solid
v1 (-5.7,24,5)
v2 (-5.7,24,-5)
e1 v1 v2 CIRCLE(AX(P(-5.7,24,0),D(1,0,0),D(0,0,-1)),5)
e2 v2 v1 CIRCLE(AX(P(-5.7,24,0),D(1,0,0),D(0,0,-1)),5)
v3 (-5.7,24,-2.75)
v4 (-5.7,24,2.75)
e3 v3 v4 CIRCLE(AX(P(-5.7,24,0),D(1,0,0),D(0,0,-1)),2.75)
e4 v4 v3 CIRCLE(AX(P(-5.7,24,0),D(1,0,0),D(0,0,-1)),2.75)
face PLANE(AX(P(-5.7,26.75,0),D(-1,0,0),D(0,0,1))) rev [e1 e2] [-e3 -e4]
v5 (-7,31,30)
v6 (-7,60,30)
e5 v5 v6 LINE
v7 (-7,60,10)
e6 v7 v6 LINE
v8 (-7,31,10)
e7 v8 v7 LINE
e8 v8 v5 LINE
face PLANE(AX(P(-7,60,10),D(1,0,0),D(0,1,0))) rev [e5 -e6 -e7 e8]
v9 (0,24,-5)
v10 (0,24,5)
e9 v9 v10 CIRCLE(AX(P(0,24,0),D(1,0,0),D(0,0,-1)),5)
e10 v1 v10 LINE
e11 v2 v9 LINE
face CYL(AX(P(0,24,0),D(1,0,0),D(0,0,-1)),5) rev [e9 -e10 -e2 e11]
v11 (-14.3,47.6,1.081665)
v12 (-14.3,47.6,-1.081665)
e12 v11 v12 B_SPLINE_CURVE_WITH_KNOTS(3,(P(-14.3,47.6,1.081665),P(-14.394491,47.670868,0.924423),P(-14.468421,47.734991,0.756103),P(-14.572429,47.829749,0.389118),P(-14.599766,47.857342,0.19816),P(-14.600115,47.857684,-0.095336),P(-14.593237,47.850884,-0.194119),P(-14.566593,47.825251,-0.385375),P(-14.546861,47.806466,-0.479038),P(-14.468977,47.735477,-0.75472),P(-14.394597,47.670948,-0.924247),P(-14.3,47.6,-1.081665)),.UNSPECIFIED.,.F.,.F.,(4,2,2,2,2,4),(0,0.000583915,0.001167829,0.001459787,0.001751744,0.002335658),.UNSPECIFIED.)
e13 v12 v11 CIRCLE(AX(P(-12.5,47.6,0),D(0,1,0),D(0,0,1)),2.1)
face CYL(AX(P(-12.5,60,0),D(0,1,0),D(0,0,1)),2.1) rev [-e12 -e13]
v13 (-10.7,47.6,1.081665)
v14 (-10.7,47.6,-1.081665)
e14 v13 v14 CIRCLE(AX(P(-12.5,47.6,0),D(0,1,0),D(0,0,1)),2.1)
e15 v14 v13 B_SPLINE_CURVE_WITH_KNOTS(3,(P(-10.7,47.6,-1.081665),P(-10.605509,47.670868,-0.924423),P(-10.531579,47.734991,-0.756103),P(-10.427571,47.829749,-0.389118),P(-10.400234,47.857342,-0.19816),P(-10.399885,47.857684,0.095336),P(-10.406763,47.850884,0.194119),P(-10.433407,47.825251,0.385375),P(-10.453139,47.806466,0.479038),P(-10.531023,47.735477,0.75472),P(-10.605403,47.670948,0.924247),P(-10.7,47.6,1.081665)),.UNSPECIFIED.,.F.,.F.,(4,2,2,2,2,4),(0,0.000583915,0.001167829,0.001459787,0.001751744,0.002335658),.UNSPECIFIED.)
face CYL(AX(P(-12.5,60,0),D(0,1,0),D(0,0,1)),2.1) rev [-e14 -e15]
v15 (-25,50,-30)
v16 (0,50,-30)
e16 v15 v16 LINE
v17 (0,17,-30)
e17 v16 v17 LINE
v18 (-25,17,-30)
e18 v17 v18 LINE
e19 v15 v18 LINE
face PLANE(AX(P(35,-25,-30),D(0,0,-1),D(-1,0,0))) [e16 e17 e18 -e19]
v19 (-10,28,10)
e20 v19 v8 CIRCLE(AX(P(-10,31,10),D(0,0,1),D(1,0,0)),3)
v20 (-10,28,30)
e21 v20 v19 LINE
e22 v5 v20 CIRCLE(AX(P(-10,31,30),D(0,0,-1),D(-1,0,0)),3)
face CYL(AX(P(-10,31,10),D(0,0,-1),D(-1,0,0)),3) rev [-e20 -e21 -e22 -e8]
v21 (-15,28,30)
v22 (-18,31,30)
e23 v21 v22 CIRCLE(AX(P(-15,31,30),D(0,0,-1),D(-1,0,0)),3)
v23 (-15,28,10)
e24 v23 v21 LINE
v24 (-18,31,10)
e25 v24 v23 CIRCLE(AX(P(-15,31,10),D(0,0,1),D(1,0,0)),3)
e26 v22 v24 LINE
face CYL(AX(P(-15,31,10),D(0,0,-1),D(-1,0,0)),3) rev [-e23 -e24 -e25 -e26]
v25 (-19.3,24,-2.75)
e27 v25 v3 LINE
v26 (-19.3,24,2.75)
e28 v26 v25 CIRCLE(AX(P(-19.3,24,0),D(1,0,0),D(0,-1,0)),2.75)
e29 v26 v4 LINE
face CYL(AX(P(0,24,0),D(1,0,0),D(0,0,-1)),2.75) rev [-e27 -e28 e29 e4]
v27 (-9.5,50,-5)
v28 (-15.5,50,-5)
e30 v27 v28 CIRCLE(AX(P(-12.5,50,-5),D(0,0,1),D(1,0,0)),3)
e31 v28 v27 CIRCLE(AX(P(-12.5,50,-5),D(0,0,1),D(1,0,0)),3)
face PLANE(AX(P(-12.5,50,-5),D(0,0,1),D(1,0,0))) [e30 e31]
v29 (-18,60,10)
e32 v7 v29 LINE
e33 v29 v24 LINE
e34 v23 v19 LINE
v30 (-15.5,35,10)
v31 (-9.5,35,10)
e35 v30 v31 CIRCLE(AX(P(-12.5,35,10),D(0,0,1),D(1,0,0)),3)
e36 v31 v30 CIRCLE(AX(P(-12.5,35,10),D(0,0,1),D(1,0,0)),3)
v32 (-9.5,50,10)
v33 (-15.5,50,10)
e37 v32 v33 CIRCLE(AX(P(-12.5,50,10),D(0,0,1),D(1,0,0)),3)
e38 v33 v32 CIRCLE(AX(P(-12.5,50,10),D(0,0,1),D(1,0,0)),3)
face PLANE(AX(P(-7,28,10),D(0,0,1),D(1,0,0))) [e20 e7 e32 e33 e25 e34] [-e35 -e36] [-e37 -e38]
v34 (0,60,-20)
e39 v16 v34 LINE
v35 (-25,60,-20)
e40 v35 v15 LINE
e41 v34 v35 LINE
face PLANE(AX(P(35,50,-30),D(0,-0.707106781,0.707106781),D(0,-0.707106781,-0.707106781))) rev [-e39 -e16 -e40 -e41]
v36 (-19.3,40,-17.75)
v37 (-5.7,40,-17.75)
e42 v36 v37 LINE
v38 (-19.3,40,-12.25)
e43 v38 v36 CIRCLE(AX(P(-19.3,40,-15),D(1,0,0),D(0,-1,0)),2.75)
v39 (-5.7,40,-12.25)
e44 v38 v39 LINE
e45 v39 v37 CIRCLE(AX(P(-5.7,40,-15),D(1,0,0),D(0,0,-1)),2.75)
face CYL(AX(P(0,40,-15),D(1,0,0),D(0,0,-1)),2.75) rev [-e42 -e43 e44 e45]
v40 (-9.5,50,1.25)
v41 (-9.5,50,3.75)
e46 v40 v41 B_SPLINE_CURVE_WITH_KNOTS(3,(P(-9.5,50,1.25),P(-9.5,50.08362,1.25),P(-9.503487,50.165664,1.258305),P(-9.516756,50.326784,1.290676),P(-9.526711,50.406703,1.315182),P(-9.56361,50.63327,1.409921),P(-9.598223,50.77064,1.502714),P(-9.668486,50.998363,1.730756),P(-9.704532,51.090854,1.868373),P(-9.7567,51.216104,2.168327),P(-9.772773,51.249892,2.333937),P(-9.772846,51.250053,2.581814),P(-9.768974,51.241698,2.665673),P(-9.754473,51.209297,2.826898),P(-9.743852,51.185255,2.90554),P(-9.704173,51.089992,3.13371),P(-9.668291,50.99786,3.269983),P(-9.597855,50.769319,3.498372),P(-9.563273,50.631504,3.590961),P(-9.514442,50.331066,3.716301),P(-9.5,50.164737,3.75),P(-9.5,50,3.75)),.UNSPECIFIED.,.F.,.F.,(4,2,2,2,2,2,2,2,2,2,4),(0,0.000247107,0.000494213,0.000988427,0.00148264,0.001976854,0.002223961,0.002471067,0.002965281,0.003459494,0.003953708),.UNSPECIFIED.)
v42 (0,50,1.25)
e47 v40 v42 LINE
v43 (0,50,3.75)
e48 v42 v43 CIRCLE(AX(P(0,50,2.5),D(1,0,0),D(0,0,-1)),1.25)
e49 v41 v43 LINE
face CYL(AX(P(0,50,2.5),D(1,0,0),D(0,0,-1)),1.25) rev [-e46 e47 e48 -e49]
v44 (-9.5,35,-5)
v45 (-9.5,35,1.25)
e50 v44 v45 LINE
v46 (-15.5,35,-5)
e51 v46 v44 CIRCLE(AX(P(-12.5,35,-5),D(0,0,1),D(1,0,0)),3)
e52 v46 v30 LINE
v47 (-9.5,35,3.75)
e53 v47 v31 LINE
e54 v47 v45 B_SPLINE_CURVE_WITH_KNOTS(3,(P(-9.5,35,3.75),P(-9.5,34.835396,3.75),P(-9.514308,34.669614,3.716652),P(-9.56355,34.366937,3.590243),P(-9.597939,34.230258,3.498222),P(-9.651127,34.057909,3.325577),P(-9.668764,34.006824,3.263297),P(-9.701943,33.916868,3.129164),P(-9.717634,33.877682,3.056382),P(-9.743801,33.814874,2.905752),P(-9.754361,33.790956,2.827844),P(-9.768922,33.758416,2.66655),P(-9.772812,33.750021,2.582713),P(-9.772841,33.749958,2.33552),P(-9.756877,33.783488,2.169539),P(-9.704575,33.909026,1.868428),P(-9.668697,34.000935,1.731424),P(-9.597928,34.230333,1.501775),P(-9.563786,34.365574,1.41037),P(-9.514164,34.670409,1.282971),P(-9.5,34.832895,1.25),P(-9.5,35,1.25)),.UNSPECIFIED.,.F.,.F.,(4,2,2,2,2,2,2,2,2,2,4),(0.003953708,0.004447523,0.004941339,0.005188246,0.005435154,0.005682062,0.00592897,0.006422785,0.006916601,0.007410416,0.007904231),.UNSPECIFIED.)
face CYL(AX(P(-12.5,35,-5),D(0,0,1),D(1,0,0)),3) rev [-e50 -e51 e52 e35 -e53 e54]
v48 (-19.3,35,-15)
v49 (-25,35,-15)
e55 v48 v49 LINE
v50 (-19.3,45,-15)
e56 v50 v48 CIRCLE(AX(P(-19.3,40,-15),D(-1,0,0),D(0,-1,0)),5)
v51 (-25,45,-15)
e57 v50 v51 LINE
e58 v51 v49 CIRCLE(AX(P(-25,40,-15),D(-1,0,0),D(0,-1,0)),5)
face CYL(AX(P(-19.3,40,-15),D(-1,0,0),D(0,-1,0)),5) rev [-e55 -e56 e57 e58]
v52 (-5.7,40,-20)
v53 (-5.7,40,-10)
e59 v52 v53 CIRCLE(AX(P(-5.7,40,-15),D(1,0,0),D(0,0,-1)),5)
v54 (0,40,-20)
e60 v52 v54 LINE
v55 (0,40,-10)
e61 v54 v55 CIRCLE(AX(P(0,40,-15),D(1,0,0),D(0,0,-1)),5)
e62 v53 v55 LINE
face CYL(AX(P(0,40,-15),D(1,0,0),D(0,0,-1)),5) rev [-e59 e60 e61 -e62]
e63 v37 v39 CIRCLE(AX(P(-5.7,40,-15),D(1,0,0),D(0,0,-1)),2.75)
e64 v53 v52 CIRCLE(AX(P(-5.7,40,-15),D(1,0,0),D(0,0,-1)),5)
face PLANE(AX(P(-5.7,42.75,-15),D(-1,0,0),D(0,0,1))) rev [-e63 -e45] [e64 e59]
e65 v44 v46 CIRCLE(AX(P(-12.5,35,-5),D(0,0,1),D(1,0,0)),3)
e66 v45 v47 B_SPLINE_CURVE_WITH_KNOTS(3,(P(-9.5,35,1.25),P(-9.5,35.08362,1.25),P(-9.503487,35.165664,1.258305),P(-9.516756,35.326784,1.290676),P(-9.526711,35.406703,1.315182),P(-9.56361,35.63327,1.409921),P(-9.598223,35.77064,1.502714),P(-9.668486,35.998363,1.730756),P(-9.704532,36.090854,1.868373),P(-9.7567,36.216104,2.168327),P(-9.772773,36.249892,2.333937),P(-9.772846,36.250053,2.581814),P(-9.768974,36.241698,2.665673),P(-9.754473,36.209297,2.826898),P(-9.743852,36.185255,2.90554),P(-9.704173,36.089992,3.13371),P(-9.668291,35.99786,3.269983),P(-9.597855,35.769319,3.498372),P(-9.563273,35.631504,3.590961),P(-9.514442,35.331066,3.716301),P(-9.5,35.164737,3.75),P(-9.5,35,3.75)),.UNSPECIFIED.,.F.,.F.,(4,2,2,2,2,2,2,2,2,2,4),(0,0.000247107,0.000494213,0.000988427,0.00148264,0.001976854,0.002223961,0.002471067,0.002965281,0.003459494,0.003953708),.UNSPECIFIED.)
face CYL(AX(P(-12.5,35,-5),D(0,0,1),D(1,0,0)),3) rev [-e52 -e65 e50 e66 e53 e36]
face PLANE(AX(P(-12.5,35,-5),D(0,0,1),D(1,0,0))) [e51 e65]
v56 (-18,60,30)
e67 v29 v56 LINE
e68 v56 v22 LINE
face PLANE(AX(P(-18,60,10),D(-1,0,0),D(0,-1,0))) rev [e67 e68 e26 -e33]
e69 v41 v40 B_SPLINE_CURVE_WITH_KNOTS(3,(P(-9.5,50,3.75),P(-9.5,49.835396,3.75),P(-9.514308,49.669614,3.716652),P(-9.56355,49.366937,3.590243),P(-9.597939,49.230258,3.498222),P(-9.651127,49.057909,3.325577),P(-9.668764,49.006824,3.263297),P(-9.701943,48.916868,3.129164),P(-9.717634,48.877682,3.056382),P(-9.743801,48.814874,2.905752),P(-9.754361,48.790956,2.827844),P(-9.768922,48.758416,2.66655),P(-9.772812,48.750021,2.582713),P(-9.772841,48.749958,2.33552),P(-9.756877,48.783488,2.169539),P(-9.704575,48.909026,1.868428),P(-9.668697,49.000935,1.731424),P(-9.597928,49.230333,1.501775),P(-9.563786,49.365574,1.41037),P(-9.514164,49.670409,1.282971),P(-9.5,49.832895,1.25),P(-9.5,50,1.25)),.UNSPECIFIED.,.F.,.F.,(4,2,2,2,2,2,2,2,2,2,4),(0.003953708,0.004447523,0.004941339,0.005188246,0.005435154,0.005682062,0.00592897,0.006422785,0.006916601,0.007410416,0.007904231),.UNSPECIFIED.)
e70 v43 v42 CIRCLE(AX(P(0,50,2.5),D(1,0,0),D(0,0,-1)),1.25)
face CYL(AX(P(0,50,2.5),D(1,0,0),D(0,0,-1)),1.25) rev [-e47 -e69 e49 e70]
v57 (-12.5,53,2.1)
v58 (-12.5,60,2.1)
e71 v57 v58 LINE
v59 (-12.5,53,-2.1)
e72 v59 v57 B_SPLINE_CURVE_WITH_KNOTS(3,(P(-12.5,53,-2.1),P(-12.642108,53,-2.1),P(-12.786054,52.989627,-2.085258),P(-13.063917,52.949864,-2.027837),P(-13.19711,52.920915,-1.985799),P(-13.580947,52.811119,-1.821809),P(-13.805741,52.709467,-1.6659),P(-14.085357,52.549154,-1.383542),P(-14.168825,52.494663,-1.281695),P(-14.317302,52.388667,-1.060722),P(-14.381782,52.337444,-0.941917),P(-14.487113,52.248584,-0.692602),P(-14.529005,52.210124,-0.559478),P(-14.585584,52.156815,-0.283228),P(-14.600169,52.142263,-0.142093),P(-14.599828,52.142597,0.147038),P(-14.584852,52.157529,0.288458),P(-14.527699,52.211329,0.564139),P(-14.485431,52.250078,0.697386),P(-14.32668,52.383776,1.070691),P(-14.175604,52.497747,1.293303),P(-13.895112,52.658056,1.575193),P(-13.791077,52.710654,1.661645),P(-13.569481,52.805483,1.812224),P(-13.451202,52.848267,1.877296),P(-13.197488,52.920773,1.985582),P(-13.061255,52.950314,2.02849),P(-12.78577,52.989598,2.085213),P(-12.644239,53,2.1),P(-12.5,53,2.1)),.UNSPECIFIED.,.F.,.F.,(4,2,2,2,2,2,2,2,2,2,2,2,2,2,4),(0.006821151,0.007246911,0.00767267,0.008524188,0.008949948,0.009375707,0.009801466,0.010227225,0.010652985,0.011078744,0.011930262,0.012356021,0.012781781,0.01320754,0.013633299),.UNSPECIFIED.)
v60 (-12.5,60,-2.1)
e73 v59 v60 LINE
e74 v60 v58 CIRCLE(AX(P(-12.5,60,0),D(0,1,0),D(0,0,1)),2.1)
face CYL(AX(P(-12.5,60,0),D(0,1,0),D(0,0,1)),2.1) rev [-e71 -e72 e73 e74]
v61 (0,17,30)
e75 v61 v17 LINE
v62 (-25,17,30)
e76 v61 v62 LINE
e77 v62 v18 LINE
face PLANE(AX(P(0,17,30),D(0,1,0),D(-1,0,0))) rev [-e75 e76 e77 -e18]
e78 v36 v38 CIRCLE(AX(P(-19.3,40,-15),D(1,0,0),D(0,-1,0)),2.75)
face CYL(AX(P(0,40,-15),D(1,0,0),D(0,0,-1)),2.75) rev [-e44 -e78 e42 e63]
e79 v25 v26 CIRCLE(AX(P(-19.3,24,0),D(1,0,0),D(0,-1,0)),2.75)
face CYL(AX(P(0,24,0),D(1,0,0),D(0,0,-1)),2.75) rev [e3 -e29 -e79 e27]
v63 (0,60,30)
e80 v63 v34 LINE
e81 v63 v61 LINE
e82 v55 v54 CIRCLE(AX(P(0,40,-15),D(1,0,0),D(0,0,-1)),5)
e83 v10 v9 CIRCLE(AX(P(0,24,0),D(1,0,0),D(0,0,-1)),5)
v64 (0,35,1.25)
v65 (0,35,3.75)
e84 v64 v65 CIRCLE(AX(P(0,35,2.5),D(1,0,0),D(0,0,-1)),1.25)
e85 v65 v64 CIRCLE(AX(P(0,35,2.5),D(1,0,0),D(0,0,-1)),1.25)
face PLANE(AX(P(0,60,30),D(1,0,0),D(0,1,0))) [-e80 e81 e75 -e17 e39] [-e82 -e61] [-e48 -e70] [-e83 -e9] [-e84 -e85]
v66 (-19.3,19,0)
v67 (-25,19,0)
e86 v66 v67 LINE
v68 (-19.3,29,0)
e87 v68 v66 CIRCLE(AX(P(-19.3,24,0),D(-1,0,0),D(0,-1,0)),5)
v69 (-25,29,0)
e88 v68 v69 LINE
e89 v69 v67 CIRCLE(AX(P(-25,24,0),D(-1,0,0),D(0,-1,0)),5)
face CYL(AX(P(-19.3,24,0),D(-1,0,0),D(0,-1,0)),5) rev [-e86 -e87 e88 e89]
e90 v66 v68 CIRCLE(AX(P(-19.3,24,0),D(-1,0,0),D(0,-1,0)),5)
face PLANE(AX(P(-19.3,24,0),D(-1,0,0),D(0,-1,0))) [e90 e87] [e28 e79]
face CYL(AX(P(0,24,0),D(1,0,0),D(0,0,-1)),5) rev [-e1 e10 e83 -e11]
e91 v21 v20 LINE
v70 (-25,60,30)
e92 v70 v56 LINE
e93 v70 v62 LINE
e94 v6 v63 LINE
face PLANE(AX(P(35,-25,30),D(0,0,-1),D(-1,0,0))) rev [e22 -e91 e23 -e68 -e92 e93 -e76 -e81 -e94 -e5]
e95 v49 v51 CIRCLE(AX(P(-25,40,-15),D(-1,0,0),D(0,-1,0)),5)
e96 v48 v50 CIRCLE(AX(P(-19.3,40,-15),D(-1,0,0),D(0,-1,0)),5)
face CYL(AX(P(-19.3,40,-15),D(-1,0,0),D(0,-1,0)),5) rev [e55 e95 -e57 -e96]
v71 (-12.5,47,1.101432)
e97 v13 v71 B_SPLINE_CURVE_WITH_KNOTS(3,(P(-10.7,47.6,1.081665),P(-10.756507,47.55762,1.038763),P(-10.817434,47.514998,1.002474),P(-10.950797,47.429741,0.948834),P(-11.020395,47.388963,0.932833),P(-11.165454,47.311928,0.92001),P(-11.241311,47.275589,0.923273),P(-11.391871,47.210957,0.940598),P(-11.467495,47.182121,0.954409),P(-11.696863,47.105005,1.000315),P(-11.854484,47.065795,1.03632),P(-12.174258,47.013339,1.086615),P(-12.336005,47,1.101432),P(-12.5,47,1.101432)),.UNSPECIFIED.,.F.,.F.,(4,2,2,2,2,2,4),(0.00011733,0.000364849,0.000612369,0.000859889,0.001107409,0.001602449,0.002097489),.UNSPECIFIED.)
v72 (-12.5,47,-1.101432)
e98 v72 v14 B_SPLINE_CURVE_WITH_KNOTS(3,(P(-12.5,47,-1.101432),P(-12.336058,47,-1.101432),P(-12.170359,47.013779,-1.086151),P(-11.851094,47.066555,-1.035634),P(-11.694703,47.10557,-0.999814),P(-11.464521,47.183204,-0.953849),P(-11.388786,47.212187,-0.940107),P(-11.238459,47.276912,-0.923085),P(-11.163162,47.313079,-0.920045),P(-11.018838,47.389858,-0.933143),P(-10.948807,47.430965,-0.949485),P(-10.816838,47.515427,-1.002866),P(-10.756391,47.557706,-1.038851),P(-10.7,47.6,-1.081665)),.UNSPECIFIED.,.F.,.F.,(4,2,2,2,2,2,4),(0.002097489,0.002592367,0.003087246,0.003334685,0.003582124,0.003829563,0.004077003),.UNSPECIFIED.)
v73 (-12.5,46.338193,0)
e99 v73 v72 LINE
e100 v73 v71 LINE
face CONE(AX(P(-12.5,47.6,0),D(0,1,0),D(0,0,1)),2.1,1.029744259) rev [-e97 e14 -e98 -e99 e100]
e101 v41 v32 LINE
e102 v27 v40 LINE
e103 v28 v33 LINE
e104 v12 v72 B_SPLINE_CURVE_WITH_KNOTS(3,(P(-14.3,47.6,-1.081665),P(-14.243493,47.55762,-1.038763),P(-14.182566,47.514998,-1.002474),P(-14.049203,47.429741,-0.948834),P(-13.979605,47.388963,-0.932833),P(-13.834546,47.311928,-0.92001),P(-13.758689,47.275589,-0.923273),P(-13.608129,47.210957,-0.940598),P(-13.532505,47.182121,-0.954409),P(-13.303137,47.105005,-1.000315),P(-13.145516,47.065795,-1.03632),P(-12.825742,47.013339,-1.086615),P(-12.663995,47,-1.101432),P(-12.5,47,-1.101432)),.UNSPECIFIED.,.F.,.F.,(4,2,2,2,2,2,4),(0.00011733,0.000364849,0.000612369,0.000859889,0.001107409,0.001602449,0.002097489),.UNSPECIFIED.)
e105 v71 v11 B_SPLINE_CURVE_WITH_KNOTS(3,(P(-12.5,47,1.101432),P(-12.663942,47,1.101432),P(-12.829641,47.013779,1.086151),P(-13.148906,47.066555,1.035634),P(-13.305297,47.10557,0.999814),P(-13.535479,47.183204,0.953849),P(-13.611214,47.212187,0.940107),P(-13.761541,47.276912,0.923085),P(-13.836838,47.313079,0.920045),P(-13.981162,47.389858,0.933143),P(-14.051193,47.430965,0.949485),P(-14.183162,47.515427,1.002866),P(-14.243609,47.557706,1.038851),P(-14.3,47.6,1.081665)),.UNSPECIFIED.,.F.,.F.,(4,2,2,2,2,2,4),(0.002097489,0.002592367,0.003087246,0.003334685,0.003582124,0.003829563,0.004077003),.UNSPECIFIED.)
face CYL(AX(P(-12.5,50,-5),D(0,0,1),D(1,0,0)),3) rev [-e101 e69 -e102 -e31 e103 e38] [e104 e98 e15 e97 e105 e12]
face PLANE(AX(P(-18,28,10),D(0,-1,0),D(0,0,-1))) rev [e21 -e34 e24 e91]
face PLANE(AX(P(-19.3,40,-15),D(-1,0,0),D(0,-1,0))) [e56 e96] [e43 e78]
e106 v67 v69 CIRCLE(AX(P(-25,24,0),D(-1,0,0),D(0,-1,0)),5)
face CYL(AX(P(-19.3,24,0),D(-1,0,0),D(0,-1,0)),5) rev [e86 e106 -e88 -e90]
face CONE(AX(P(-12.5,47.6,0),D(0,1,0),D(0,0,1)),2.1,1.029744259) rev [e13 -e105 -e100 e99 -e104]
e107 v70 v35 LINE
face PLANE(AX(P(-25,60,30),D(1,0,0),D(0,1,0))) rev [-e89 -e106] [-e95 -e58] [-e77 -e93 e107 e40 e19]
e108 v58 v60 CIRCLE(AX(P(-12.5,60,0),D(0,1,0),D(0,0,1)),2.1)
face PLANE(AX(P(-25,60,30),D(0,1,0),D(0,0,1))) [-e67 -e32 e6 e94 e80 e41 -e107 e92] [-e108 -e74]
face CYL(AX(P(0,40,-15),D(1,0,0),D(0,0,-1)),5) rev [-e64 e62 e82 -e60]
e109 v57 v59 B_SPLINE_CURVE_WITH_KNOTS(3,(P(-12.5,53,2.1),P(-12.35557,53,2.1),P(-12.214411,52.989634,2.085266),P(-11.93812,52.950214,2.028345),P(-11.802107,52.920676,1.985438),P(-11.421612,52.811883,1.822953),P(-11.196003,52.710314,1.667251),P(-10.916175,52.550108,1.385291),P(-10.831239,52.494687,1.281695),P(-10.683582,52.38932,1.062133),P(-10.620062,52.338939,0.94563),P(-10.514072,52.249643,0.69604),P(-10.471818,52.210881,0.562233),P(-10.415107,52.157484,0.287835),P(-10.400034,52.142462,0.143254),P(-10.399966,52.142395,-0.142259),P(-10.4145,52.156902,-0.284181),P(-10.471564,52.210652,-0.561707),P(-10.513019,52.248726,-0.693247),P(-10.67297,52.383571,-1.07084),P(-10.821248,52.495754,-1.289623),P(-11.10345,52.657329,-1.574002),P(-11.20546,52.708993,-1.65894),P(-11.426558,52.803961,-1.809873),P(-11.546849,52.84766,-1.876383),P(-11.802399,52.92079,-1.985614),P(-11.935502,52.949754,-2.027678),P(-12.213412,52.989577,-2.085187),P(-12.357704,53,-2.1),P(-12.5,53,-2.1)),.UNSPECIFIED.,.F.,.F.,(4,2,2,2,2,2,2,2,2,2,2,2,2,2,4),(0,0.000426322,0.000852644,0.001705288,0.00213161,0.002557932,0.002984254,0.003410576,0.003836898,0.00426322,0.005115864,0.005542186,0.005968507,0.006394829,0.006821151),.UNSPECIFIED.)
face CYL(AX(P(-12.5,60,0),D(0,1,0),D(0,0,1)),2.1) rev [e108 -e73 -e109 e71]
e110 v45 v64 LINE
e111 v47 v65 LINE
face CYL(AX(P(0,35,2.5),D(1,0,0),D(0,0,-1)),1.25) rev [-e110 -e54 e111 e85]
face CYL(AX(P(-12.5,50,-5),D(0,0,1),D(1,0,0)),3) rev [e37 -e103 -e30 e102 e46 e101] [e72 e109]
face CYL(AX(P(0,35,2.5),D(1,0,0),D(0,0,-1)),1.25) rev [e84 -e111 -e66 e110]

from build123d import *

# Parameters (mm, degrees)
EXTRUDE_THIN1_DEPTH                                  = 30
SKETCH2_W                                            = 60
SKETCH2_H                                            = 12.5
CUT_EXTRUDE1_DEPTH                                   = 92.787798753
SKETCH3_W                                            = 11
SKETCH3_H                                            = 32
CUT_EXTRUDE2_DEPTH                                   = 20
FILLET1_R                                            = 3
SKETCH6_R                                            = 3
CUT_EXTRUDE3_DEPTH                                   = 15
M3_TAPPED_HOLE2_D                                    = 2.5
M3_TAPPED_HOLE2_DEPTH                                = 11.5
M3_TAPPED_HOLE2_TIP                                  = 0.751075774
M5_TAPPED_HOLE1_D                                    = 4.2
M5_TAPPED_HOLE1_DEPTH                                = 12.4
M5_TAPPED_HOLE1_TIP                                  = 1.2618073
CUT_EXTRUDE4_DEPTH                                   = 86.914201472
SKETCH13_W                                           = 35
SKETCH13_H                                           = 12.5
CUT_EXTRUDE6_DEPTH                                   = 1
SKETCH14_W                                           = 10
SKETCH14_H                                           = 59
CUT_EXTRUDE7_DEPTH                                   = 1.5
CHAMFER1_SIZE                                        = 10
SKETCH15_W                                           = 35
SKETCH15_H                                           = 12.5
CUT_EXTRUDE8_DEPTH                                   = 92.137259186
HOLE_SIZE_PER_SOCKET_HEAD_CAP_SCREW_TYPE_D           = 5.5
HOLE_SIZE_PER_SOCKET_HEAD_CAP_SCREW_TYPE_CBORE_D     = 10
HOLE_SIZE_PER_SOCKET_HEAD_CAP_SCREW_TYPE_CBORE_DEPTH = 5.7
SKETCH18_W                                           = 60
SKETCH18_H                                           = 29.5
CUT_EXTRUDE9_DEPTH                                   = 72.589105435
CUT_EXTRUDE10_START                                  = -5.7
SKETCH19_R                                           = 5
CUT_EXTRUDE10_DEPTH                                  = 5.7


with BuildPart() as part:
    # Sketch1 → Extrude-Thin1 (new, symmetric)
    with BuildSketch(Plane.XY):
        Polygon((0, 60), (0, 0), (35, 0), (35, -25), (-25, -25), (-25, 60), align=None)
    extrude(amount=EXTRUDE_THIN1_DEPTH, both=True)

    # Sketch2 → Cut-Extrude1 (cut, through all)
    with BuildSketch(Plane.XY.offset(30)):
        with Locations((5, -18.75)):
            Rectangle(SKETCH2_W, SKETCH2_H)
    extrude(amount=-CUT_EXTRUDE1_DEPTH, mode=Mode.SUBTRACT)

    # Sketch3 → Cut-Extrude2 (cut)
    with BuildSketch(Plane.XY.offset(30)):
        with Locations((-12.5, 44)):
            Rectangle(SKETCH3_W, SKETCH3_H)
    extrude(amount=-CUT_EXTRUDE2_DEPTH, mode=Mode.SUBTRACT)

    # Fillet1
    fillet1_edges = [part.edges().sort_by_distance(p)[0] for p in [
        (-7, 28, 20),
        (-18, 28, 20),
    ]]
    fillet(fillet1_edges, radius=FILLET1_R)

    # Sketch6 → Cut-Extrude3 (cut)
    with BuildSketch(Plane.XY.offset(10)):
        with Locations((-12.5, 50)):
            Circle(SKETCH6_R)
        with Locations((-12.5, 35)):
            Circle(SKETCH6_R)
    extrude(amount=-CUT_EXTRUDE3_DEPTH, mode=Mode.SUBTRACT)

    # M3 Tapped Hole2
    with Locations(Plane(origin=(0, 0, 0), x_dir=(0, 0, -1), z_dir=(1, 0, 0))):
        with Locations((-2.5, 50), (-2.5, 35)):
            Hole(M3_TAPPED_HOLE2_D / 2, depth=M3_TAPPED_HOLE2_DEPTH)
            with Locations((0, 0, -(M3_TAPPED_HOLE2_DEPTH + M3_TAPPED_HOLE2_TIP / 2))):  # 118° drill point
                Cone(0, M3_TAPPED_HOLE2_D / 2, M3_TAPPED_HOLE2_TIP, mode=Mode.SUBTRACT)

    # M5 Tapped Hole1
    with Locations(Plane(origin=(0, 60, 0), x_dir=(-1, 0, 0), z_dir=(0, 1, 0))):
        with Locations((12.5, 0)):
            Hole(M5_TAPPED_HOLE1_D / 2, depth=M5_TAPPED_HOLE1_DEPTH)
            with Locations((0, 0, -(M5_TAPPED_HOLE1_DEPTH + M5_TAPPED_HOLE1_TIP / 2))):  # 118° drill point
                Cone(0, M5_TAPPED_HOLE1_D / 2, M5_TAPPED_HOLE1_TIP, mode=Mode.SUBTRACT)

    # Sketch11 → Cut-Extrude4 (cut, through all)
    with BuildSketch(Plane.XZ.offset(12.5)):
        with BuildLine():
            Line((32.25, -5), (32.25, -25))
            ThreePointArc((32.25, -25), (30, -27.25), (27.75, -25))
            Line((27.75, -25), (27.75, -5))
            ThreePointArc((27.75, -5), (30, -2.75), (32.25, -5))
        make_face()
    extrude(amount=-CUT_EXTRUDE4_DEPTH, mode=Mode.SUBTRACT)

    # Sketch13 → Cut-Extrude6 (cut)
    with BuildSketch(Plane.XY.offset(30)):
        with Locations((17.5, -6.25)):
            Rectangle(SKETCH13_W, SKETCH13_H)
    extrude(amount=-CUT_EXTRUDE6_DEPTH, mode=Mode.SUBTRACT)

    # Sketch14 → Cut-Extrude7 (cut)
    with BuildSketch(Plane(origin=(0, 0, 0), x_dir=(1, 0, 0), z_dir=(0, 1, 0))):
        with Locations((30, 0.5)):
            Rectangle(SKETCH14_W, SKETCH14_H)
    extrude(amount=-CUT_EXTRUDE7_DEPTH, mode=Mode.SUBTRACT)

    # Chamfer1
    chamfer1_edges = [part.edges().sort_by_distance(p)[0] for p in [
        (-12.5, 60, -30),
    ]]
    chamfer(chamfer1_edges, length=CHAMFER1_SIZE)

    # Sketch15 → Cut-Extrude8 (cut, through all)
    with BuildSketch(Plane.XY.offset(29)):
        with Locations((17.5, -6.25)):
            Rectangle(SKETCH15_W, SKETCH15_H)
    extrude(amount=-CUT_EXTRUDE8_DEPTH, mode=Mode.SUBTRACT)

    # Hole Size per Socket Head Cap Screw Type1 (through all)
    with Locations(Plane(origin=(0, 0, 0), x_dir=(0, 0, -1), z_dir=(1, 0, 0))):
        with Locations((0, 24), (15, 40)):
            CounterBoreHole(HOLE_SIZE_PER_SOCKET_HEAD_CAP_SCREW_TYPE_D / 2, HOLE_SIZE_PER_SOCKET_HEAD_CAP_SCREW_TYPE_CBORE_D / 2, HOLE_SIZE_PER_SOCKET_HEAD_CAP_SCREW_TYPE_CBORE_DEPTH)

    # Sketch18 → Cut-Extrude9 (cut, through all)
    with BuildSketch(Plane.ZY.offset(25)):
        with Locations((0, 2.25)):
            Rectangle(SKETCH18_W, SKETCH18_H)
    extrude(amount=-CUT_EXTRUDE9_DEPTH, mode=Mode.SUBTRACT)

    # Sketch19 → Cut-Extrude10 (cut)
    with BuildSketch(Plane.ZY.offset(25).offset(CUT_EXTRUDE10_START)):
        with Locations(Location((-15, 40, 0), (0, 0, 180))):
            Circle(SKETCH19_R)
        with Locations(Location((0, 24, 0), (0, 0, 180))):
            Circle(SKETCH19_R)
    extrude(amount=CUT_EXTRUDE10_DEPTH, mode=Mode.SUBTRACT)


solid = part.part
